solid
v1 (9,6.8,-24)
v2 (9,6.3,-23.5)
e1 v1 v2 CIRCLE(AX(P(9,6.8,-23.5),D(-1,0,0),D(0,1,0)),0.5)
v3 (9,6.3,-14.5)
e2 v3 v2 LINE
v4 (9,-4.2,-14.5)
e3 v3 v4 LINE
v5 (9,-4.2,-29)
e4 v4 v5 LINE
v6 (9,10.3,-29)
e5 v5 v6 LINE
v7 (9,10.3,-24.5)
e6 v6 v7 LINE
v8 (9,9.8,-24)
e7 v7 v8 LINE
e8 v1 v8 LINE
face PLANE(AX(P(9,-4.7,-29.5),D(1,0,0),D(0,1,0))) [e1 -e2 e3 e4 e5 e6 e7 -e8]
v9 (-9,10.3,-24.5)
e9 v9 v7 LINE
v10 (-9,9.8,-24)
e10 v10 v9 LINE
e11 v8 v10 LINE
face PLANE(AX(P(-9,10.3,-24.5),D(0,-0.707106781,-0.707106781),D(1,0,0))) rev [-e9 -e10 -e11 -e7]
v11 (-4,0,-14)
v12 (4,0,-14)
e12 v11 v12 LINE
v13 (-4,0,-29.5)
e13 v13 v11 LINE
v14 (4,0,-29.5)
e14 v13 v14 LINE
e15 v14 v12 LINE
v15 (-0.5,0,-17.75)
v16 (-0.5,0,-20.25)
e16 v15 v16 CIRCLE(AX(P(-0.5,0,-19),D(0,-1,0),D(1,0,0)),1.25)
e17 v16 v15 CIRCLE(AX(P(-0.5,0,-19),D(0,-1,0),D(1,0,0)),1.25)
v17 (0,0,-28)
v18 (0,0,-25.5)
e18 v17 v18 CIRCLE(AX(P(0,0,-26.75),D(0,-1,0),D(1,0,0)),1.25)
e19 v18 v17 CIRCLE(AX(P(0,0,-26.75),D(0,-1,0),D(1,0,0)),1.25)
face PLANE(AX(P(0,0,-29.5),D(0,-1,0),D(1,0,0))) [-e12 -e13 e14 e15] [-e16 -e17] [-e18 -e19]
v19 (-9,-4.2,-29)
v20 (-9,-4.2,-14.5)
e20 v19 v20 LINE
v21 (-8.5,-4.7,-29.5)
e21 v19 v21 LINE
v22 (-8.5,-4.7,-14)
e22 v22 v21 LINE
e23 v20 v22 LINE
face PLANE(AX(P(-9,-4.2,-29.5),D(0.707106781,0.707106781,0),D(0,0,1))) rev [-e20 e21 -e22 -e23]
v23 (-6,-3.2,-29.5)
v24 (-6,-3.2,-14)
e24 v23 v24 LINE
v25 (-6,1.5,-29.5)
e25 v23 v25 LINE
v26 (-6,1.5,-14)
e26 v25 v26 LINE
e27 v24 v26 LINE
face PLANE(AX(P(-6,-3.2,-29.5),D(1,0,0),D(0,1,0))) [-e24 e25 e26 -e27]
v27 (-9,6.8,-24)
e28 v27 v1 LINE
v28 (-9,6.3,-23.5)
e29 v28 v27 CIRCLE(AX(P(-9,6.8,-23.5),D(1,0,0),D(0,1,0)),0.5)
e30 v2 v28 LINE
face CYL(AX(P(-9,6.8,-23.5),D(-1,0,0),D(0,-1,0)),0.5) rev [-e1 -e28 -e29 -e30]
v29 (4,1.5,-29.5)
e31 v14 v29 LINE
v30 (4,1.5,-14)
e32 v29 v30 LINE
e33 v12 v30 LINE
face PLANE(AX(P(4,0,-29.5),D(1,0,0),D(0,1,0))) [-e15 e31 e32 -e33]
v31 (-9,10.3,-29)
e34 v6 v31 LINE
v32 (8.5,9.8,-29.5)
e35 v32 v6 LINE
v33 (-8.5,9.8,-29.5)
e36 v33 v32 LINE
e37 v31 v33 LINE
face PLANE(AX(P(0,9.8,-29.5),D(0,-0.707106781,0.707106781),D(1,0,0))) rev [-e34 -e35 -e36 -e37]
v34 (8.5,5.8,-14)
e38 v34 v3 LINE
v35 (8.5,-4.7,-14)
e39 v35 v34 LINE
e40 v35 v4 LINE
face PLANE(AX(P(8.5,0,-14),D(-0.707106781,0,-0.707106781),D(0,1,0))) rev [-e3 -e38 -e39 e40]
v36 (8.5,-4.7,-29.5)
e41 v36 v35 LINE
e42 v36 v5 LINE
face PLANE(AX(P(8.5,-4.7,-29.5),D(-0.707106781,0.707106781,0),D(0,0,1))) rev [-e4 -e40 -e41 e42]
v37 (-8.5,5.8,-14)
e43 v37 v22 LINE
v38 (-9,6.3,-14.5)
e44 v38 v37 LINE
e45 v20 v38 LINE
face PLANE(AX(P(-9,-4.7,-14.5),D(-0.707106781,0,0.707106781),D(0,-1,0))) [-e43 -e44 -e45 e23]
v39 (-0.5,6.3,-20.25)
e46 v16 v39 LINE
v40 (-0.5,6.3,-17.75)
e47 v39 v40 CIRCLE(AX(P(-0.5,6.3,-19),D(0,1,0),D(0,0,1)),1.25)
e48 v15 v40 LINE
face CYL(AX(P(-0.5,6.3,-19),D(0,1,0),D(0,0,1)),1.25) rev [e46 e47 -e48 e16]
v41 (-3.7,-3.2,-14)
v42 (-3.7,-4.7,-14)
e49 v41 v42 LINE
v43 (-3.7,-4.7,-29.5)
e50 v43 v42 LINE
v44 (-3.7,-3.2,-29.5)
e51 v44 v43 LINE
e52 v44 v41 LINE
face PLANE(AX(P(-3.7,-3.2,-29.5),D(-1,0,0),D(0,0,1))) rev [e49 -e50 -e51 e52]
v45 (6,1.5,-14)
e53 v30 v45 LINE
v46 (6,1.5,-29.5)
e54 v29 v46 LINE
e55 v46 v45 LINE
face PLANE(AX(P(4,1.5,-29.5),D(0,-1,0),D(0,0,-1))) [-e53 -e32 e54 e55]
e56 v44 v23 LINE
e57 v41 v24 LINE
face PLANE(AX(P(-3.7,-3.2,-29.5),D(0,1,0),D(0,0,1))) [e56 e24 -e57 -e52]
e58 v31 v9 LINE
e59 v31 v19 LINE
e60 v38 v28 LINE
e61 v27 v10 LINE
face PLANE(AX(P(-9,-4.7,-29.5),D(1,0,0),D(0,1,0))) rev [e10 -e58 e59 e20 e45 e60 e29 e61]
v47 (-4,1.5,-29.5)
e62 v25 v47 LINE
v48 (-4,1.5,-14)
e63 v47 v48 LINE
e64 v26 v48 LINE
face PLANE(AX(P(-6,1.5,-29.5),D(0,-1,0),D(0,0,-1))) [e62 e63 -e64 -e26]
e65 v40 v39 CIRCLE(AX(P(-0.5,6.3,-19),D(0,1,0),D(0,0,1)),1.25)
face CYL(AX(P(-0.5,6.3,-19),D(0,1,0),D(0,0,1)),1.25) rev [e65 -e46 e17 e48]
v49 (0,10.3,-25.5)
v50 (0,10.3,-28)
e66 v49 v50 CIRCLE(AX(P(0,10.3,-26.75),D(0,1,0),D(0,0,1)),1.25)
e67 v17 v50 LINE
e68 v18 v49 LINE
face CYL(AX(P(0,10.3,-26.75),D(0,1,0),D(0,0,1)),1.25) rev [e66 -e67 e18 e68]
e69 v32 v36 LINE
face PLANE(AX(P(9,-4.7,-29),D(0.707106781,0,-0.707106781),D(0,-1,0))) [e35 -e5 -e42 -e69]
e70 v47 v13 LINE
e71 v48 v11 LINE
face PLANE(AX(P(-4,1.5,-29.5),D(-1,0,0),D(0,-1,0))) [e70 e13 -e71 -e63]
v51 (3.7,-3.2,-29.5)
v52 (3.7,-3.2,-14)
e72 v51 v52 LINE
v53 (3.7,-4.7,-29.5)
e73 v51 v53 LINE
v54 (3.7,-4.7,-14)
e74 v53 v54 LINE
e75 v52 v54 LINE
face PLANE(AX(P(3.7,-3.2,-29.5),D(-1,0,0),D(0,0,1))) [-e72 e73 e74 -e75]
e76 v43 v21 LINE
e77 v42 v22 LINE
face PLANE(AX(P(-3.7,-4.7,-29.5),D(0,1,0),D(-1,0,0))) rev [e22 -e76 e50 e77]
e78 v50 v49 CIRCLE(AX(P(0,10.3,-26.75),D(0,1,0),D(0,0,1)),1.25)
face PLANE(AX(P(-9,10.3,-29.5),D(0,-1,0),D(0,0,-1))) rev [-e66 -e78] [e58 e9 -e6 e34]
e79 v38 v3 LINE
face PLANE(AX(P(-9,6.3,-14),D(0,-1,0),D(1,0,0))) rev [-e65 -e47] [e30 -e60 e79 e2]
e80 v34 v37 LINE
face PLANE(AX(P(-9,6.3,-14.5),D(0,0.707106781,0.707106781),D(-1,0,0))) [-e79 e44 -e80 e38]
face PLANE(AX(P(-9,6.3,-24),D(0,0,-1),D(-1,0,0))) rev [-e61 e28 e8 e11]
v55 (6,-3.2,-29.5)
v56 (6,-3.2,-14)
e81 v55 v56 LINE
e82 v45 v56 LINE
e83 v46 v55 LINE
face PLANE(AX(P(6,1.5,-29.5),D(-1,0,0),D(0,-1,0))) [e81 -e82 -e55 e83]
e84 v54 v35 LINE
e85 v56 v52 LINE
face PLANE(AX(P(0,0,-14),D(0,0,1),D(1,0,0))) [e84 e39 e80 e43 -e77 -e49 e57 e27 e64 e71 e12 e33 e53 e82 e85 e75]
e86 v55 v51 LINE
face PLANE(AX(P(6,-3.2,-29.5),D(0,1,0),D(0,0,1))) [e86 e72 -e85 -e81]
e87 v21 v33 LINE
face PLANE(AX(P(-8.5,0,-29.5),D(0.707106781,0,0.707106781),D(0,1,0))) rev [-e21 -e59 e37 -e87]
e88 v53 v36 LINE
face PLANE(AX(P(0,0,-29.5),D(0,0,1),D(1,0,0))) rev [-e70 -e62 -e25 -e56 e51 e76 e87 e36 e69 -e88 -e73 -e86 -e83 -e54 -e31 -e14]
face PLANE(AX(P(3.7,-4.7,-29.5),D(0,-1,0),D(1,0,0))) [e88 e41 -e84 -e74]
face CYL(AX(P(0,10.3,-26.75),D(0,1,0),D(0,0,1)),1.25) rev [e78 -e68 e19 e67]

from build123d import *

# Parameters (mm, degrees)
BOSS_EXTRUDE1_START   = -14
BOSS_EXTRUDE1_DEPTH   = 15.5
SKETCH2_W             = 10
SKETCH2_H             = 4
CUT_EXTRUDE1_DEPTH    = 37.060227398
M3_TAPPED_HOLE1_D     = 2.5
M3_TAPPED_HOLE1_DEPTH = 8.5
M3_TAPPED_HOLE1_TIP   = 0.751075774
M3_TAPPED_HOLE2_D     = 2.5
CHAMFER1_SIZE         = 0.5
FILLET1_R             = 0.5


with BuildPart() as part:
    # Sketch1 → Boss-Extrude1 (new body)
    with BuildSketch(Plane.XY.offset(BOSS_EXTRUDE1_START)):
        Polygon((-3.7, -3.2), (-3.7, -4.7), (-9, -4.7), (-9, 10.3), (9, 10.3), (9, -4.7), (3.7, -4.7), (3.7, -3.2), (6, -3.2), (6, 1.5), (4, 1.5), (4, 0), (0, 0), (-4, 0), (-4, 1.5), (-6, 1.5), (-6, -3.2), align=None)
    extrude(amount=-BOSS_EXTRUDE1_DEPTH)

    # Sketch2 → Cut-Extrude1 (cut, through all)
    with BuildSketch(Plane(origin=(9, 0, 0), x_dir=(0, 0, -1), z_dir=(1, 0, 0))):
        with Locations((19, 8.3)):
            Rectangle(SKETCH2_W, SKETCH2_H)
    extrude(amount=-CUT_EXTRUDE1_DEPTH, mode=Mode.SUBTRACT)

    # M3 Tapped Hole1
    with Locations(Plane(origin=(0, 6.3, 0), x_dir=(1, 0, 0), z_dir=(0, 1, 0))):
        with Locations((-0.5, 19)):
            Hole(M3_TAPPED_HOLE1_D / 2, depth=M3_TAPPED_HOLE1_DEPTH)
            with Locations((0, 0, -(M3_TAPPED_HOLE1_DEPTH + M3_TAPPED_HOLE1_TIP / 2))):  # 118° drill point
                Cone(0, M3_TAPPED_HOLE1_D / 2, M3_TAPPED_HOLE1_TIP, mode=Mode.SUBTRACT)

    # M3 Tapped Hole2 (through all)
    with Locations(Plane(origin=(0, 10.3, 0), x_dir=(1, 0, 0), z_dir=(0, 1, 0))):
        with Locations((0, 26.75)):
            Hole(M3_TAPPED_HOLE2_D / 2)

    # Chamfer1
    chamfer1_edges = [part.edges().sort_by_distance(p)[0] for p in [
        (0, 10.3, -29.5),
        (-9, 2.8, -29.5),
        (-9, 0.8, -14),
        (9, 0.8, -14),
        (-9, -4.7, -21.75),
        (9, -4.7, -21.75),
        (0, 6.3, -14),
        (0, 10.3, -24),
        (9, 2.8, -29.5),
    ]]
    chamfer(chamfer1_edges, length=CHAMFER1_SIZE)

    # Fillet1
    fillet1_edges = [part.edges().sort_by_distance(p)[0] for p in [
        (0, 6.3, -24),
    ]]
    fillet(fillet1_edges, radius=FILLET1_R)


solid = part.part
